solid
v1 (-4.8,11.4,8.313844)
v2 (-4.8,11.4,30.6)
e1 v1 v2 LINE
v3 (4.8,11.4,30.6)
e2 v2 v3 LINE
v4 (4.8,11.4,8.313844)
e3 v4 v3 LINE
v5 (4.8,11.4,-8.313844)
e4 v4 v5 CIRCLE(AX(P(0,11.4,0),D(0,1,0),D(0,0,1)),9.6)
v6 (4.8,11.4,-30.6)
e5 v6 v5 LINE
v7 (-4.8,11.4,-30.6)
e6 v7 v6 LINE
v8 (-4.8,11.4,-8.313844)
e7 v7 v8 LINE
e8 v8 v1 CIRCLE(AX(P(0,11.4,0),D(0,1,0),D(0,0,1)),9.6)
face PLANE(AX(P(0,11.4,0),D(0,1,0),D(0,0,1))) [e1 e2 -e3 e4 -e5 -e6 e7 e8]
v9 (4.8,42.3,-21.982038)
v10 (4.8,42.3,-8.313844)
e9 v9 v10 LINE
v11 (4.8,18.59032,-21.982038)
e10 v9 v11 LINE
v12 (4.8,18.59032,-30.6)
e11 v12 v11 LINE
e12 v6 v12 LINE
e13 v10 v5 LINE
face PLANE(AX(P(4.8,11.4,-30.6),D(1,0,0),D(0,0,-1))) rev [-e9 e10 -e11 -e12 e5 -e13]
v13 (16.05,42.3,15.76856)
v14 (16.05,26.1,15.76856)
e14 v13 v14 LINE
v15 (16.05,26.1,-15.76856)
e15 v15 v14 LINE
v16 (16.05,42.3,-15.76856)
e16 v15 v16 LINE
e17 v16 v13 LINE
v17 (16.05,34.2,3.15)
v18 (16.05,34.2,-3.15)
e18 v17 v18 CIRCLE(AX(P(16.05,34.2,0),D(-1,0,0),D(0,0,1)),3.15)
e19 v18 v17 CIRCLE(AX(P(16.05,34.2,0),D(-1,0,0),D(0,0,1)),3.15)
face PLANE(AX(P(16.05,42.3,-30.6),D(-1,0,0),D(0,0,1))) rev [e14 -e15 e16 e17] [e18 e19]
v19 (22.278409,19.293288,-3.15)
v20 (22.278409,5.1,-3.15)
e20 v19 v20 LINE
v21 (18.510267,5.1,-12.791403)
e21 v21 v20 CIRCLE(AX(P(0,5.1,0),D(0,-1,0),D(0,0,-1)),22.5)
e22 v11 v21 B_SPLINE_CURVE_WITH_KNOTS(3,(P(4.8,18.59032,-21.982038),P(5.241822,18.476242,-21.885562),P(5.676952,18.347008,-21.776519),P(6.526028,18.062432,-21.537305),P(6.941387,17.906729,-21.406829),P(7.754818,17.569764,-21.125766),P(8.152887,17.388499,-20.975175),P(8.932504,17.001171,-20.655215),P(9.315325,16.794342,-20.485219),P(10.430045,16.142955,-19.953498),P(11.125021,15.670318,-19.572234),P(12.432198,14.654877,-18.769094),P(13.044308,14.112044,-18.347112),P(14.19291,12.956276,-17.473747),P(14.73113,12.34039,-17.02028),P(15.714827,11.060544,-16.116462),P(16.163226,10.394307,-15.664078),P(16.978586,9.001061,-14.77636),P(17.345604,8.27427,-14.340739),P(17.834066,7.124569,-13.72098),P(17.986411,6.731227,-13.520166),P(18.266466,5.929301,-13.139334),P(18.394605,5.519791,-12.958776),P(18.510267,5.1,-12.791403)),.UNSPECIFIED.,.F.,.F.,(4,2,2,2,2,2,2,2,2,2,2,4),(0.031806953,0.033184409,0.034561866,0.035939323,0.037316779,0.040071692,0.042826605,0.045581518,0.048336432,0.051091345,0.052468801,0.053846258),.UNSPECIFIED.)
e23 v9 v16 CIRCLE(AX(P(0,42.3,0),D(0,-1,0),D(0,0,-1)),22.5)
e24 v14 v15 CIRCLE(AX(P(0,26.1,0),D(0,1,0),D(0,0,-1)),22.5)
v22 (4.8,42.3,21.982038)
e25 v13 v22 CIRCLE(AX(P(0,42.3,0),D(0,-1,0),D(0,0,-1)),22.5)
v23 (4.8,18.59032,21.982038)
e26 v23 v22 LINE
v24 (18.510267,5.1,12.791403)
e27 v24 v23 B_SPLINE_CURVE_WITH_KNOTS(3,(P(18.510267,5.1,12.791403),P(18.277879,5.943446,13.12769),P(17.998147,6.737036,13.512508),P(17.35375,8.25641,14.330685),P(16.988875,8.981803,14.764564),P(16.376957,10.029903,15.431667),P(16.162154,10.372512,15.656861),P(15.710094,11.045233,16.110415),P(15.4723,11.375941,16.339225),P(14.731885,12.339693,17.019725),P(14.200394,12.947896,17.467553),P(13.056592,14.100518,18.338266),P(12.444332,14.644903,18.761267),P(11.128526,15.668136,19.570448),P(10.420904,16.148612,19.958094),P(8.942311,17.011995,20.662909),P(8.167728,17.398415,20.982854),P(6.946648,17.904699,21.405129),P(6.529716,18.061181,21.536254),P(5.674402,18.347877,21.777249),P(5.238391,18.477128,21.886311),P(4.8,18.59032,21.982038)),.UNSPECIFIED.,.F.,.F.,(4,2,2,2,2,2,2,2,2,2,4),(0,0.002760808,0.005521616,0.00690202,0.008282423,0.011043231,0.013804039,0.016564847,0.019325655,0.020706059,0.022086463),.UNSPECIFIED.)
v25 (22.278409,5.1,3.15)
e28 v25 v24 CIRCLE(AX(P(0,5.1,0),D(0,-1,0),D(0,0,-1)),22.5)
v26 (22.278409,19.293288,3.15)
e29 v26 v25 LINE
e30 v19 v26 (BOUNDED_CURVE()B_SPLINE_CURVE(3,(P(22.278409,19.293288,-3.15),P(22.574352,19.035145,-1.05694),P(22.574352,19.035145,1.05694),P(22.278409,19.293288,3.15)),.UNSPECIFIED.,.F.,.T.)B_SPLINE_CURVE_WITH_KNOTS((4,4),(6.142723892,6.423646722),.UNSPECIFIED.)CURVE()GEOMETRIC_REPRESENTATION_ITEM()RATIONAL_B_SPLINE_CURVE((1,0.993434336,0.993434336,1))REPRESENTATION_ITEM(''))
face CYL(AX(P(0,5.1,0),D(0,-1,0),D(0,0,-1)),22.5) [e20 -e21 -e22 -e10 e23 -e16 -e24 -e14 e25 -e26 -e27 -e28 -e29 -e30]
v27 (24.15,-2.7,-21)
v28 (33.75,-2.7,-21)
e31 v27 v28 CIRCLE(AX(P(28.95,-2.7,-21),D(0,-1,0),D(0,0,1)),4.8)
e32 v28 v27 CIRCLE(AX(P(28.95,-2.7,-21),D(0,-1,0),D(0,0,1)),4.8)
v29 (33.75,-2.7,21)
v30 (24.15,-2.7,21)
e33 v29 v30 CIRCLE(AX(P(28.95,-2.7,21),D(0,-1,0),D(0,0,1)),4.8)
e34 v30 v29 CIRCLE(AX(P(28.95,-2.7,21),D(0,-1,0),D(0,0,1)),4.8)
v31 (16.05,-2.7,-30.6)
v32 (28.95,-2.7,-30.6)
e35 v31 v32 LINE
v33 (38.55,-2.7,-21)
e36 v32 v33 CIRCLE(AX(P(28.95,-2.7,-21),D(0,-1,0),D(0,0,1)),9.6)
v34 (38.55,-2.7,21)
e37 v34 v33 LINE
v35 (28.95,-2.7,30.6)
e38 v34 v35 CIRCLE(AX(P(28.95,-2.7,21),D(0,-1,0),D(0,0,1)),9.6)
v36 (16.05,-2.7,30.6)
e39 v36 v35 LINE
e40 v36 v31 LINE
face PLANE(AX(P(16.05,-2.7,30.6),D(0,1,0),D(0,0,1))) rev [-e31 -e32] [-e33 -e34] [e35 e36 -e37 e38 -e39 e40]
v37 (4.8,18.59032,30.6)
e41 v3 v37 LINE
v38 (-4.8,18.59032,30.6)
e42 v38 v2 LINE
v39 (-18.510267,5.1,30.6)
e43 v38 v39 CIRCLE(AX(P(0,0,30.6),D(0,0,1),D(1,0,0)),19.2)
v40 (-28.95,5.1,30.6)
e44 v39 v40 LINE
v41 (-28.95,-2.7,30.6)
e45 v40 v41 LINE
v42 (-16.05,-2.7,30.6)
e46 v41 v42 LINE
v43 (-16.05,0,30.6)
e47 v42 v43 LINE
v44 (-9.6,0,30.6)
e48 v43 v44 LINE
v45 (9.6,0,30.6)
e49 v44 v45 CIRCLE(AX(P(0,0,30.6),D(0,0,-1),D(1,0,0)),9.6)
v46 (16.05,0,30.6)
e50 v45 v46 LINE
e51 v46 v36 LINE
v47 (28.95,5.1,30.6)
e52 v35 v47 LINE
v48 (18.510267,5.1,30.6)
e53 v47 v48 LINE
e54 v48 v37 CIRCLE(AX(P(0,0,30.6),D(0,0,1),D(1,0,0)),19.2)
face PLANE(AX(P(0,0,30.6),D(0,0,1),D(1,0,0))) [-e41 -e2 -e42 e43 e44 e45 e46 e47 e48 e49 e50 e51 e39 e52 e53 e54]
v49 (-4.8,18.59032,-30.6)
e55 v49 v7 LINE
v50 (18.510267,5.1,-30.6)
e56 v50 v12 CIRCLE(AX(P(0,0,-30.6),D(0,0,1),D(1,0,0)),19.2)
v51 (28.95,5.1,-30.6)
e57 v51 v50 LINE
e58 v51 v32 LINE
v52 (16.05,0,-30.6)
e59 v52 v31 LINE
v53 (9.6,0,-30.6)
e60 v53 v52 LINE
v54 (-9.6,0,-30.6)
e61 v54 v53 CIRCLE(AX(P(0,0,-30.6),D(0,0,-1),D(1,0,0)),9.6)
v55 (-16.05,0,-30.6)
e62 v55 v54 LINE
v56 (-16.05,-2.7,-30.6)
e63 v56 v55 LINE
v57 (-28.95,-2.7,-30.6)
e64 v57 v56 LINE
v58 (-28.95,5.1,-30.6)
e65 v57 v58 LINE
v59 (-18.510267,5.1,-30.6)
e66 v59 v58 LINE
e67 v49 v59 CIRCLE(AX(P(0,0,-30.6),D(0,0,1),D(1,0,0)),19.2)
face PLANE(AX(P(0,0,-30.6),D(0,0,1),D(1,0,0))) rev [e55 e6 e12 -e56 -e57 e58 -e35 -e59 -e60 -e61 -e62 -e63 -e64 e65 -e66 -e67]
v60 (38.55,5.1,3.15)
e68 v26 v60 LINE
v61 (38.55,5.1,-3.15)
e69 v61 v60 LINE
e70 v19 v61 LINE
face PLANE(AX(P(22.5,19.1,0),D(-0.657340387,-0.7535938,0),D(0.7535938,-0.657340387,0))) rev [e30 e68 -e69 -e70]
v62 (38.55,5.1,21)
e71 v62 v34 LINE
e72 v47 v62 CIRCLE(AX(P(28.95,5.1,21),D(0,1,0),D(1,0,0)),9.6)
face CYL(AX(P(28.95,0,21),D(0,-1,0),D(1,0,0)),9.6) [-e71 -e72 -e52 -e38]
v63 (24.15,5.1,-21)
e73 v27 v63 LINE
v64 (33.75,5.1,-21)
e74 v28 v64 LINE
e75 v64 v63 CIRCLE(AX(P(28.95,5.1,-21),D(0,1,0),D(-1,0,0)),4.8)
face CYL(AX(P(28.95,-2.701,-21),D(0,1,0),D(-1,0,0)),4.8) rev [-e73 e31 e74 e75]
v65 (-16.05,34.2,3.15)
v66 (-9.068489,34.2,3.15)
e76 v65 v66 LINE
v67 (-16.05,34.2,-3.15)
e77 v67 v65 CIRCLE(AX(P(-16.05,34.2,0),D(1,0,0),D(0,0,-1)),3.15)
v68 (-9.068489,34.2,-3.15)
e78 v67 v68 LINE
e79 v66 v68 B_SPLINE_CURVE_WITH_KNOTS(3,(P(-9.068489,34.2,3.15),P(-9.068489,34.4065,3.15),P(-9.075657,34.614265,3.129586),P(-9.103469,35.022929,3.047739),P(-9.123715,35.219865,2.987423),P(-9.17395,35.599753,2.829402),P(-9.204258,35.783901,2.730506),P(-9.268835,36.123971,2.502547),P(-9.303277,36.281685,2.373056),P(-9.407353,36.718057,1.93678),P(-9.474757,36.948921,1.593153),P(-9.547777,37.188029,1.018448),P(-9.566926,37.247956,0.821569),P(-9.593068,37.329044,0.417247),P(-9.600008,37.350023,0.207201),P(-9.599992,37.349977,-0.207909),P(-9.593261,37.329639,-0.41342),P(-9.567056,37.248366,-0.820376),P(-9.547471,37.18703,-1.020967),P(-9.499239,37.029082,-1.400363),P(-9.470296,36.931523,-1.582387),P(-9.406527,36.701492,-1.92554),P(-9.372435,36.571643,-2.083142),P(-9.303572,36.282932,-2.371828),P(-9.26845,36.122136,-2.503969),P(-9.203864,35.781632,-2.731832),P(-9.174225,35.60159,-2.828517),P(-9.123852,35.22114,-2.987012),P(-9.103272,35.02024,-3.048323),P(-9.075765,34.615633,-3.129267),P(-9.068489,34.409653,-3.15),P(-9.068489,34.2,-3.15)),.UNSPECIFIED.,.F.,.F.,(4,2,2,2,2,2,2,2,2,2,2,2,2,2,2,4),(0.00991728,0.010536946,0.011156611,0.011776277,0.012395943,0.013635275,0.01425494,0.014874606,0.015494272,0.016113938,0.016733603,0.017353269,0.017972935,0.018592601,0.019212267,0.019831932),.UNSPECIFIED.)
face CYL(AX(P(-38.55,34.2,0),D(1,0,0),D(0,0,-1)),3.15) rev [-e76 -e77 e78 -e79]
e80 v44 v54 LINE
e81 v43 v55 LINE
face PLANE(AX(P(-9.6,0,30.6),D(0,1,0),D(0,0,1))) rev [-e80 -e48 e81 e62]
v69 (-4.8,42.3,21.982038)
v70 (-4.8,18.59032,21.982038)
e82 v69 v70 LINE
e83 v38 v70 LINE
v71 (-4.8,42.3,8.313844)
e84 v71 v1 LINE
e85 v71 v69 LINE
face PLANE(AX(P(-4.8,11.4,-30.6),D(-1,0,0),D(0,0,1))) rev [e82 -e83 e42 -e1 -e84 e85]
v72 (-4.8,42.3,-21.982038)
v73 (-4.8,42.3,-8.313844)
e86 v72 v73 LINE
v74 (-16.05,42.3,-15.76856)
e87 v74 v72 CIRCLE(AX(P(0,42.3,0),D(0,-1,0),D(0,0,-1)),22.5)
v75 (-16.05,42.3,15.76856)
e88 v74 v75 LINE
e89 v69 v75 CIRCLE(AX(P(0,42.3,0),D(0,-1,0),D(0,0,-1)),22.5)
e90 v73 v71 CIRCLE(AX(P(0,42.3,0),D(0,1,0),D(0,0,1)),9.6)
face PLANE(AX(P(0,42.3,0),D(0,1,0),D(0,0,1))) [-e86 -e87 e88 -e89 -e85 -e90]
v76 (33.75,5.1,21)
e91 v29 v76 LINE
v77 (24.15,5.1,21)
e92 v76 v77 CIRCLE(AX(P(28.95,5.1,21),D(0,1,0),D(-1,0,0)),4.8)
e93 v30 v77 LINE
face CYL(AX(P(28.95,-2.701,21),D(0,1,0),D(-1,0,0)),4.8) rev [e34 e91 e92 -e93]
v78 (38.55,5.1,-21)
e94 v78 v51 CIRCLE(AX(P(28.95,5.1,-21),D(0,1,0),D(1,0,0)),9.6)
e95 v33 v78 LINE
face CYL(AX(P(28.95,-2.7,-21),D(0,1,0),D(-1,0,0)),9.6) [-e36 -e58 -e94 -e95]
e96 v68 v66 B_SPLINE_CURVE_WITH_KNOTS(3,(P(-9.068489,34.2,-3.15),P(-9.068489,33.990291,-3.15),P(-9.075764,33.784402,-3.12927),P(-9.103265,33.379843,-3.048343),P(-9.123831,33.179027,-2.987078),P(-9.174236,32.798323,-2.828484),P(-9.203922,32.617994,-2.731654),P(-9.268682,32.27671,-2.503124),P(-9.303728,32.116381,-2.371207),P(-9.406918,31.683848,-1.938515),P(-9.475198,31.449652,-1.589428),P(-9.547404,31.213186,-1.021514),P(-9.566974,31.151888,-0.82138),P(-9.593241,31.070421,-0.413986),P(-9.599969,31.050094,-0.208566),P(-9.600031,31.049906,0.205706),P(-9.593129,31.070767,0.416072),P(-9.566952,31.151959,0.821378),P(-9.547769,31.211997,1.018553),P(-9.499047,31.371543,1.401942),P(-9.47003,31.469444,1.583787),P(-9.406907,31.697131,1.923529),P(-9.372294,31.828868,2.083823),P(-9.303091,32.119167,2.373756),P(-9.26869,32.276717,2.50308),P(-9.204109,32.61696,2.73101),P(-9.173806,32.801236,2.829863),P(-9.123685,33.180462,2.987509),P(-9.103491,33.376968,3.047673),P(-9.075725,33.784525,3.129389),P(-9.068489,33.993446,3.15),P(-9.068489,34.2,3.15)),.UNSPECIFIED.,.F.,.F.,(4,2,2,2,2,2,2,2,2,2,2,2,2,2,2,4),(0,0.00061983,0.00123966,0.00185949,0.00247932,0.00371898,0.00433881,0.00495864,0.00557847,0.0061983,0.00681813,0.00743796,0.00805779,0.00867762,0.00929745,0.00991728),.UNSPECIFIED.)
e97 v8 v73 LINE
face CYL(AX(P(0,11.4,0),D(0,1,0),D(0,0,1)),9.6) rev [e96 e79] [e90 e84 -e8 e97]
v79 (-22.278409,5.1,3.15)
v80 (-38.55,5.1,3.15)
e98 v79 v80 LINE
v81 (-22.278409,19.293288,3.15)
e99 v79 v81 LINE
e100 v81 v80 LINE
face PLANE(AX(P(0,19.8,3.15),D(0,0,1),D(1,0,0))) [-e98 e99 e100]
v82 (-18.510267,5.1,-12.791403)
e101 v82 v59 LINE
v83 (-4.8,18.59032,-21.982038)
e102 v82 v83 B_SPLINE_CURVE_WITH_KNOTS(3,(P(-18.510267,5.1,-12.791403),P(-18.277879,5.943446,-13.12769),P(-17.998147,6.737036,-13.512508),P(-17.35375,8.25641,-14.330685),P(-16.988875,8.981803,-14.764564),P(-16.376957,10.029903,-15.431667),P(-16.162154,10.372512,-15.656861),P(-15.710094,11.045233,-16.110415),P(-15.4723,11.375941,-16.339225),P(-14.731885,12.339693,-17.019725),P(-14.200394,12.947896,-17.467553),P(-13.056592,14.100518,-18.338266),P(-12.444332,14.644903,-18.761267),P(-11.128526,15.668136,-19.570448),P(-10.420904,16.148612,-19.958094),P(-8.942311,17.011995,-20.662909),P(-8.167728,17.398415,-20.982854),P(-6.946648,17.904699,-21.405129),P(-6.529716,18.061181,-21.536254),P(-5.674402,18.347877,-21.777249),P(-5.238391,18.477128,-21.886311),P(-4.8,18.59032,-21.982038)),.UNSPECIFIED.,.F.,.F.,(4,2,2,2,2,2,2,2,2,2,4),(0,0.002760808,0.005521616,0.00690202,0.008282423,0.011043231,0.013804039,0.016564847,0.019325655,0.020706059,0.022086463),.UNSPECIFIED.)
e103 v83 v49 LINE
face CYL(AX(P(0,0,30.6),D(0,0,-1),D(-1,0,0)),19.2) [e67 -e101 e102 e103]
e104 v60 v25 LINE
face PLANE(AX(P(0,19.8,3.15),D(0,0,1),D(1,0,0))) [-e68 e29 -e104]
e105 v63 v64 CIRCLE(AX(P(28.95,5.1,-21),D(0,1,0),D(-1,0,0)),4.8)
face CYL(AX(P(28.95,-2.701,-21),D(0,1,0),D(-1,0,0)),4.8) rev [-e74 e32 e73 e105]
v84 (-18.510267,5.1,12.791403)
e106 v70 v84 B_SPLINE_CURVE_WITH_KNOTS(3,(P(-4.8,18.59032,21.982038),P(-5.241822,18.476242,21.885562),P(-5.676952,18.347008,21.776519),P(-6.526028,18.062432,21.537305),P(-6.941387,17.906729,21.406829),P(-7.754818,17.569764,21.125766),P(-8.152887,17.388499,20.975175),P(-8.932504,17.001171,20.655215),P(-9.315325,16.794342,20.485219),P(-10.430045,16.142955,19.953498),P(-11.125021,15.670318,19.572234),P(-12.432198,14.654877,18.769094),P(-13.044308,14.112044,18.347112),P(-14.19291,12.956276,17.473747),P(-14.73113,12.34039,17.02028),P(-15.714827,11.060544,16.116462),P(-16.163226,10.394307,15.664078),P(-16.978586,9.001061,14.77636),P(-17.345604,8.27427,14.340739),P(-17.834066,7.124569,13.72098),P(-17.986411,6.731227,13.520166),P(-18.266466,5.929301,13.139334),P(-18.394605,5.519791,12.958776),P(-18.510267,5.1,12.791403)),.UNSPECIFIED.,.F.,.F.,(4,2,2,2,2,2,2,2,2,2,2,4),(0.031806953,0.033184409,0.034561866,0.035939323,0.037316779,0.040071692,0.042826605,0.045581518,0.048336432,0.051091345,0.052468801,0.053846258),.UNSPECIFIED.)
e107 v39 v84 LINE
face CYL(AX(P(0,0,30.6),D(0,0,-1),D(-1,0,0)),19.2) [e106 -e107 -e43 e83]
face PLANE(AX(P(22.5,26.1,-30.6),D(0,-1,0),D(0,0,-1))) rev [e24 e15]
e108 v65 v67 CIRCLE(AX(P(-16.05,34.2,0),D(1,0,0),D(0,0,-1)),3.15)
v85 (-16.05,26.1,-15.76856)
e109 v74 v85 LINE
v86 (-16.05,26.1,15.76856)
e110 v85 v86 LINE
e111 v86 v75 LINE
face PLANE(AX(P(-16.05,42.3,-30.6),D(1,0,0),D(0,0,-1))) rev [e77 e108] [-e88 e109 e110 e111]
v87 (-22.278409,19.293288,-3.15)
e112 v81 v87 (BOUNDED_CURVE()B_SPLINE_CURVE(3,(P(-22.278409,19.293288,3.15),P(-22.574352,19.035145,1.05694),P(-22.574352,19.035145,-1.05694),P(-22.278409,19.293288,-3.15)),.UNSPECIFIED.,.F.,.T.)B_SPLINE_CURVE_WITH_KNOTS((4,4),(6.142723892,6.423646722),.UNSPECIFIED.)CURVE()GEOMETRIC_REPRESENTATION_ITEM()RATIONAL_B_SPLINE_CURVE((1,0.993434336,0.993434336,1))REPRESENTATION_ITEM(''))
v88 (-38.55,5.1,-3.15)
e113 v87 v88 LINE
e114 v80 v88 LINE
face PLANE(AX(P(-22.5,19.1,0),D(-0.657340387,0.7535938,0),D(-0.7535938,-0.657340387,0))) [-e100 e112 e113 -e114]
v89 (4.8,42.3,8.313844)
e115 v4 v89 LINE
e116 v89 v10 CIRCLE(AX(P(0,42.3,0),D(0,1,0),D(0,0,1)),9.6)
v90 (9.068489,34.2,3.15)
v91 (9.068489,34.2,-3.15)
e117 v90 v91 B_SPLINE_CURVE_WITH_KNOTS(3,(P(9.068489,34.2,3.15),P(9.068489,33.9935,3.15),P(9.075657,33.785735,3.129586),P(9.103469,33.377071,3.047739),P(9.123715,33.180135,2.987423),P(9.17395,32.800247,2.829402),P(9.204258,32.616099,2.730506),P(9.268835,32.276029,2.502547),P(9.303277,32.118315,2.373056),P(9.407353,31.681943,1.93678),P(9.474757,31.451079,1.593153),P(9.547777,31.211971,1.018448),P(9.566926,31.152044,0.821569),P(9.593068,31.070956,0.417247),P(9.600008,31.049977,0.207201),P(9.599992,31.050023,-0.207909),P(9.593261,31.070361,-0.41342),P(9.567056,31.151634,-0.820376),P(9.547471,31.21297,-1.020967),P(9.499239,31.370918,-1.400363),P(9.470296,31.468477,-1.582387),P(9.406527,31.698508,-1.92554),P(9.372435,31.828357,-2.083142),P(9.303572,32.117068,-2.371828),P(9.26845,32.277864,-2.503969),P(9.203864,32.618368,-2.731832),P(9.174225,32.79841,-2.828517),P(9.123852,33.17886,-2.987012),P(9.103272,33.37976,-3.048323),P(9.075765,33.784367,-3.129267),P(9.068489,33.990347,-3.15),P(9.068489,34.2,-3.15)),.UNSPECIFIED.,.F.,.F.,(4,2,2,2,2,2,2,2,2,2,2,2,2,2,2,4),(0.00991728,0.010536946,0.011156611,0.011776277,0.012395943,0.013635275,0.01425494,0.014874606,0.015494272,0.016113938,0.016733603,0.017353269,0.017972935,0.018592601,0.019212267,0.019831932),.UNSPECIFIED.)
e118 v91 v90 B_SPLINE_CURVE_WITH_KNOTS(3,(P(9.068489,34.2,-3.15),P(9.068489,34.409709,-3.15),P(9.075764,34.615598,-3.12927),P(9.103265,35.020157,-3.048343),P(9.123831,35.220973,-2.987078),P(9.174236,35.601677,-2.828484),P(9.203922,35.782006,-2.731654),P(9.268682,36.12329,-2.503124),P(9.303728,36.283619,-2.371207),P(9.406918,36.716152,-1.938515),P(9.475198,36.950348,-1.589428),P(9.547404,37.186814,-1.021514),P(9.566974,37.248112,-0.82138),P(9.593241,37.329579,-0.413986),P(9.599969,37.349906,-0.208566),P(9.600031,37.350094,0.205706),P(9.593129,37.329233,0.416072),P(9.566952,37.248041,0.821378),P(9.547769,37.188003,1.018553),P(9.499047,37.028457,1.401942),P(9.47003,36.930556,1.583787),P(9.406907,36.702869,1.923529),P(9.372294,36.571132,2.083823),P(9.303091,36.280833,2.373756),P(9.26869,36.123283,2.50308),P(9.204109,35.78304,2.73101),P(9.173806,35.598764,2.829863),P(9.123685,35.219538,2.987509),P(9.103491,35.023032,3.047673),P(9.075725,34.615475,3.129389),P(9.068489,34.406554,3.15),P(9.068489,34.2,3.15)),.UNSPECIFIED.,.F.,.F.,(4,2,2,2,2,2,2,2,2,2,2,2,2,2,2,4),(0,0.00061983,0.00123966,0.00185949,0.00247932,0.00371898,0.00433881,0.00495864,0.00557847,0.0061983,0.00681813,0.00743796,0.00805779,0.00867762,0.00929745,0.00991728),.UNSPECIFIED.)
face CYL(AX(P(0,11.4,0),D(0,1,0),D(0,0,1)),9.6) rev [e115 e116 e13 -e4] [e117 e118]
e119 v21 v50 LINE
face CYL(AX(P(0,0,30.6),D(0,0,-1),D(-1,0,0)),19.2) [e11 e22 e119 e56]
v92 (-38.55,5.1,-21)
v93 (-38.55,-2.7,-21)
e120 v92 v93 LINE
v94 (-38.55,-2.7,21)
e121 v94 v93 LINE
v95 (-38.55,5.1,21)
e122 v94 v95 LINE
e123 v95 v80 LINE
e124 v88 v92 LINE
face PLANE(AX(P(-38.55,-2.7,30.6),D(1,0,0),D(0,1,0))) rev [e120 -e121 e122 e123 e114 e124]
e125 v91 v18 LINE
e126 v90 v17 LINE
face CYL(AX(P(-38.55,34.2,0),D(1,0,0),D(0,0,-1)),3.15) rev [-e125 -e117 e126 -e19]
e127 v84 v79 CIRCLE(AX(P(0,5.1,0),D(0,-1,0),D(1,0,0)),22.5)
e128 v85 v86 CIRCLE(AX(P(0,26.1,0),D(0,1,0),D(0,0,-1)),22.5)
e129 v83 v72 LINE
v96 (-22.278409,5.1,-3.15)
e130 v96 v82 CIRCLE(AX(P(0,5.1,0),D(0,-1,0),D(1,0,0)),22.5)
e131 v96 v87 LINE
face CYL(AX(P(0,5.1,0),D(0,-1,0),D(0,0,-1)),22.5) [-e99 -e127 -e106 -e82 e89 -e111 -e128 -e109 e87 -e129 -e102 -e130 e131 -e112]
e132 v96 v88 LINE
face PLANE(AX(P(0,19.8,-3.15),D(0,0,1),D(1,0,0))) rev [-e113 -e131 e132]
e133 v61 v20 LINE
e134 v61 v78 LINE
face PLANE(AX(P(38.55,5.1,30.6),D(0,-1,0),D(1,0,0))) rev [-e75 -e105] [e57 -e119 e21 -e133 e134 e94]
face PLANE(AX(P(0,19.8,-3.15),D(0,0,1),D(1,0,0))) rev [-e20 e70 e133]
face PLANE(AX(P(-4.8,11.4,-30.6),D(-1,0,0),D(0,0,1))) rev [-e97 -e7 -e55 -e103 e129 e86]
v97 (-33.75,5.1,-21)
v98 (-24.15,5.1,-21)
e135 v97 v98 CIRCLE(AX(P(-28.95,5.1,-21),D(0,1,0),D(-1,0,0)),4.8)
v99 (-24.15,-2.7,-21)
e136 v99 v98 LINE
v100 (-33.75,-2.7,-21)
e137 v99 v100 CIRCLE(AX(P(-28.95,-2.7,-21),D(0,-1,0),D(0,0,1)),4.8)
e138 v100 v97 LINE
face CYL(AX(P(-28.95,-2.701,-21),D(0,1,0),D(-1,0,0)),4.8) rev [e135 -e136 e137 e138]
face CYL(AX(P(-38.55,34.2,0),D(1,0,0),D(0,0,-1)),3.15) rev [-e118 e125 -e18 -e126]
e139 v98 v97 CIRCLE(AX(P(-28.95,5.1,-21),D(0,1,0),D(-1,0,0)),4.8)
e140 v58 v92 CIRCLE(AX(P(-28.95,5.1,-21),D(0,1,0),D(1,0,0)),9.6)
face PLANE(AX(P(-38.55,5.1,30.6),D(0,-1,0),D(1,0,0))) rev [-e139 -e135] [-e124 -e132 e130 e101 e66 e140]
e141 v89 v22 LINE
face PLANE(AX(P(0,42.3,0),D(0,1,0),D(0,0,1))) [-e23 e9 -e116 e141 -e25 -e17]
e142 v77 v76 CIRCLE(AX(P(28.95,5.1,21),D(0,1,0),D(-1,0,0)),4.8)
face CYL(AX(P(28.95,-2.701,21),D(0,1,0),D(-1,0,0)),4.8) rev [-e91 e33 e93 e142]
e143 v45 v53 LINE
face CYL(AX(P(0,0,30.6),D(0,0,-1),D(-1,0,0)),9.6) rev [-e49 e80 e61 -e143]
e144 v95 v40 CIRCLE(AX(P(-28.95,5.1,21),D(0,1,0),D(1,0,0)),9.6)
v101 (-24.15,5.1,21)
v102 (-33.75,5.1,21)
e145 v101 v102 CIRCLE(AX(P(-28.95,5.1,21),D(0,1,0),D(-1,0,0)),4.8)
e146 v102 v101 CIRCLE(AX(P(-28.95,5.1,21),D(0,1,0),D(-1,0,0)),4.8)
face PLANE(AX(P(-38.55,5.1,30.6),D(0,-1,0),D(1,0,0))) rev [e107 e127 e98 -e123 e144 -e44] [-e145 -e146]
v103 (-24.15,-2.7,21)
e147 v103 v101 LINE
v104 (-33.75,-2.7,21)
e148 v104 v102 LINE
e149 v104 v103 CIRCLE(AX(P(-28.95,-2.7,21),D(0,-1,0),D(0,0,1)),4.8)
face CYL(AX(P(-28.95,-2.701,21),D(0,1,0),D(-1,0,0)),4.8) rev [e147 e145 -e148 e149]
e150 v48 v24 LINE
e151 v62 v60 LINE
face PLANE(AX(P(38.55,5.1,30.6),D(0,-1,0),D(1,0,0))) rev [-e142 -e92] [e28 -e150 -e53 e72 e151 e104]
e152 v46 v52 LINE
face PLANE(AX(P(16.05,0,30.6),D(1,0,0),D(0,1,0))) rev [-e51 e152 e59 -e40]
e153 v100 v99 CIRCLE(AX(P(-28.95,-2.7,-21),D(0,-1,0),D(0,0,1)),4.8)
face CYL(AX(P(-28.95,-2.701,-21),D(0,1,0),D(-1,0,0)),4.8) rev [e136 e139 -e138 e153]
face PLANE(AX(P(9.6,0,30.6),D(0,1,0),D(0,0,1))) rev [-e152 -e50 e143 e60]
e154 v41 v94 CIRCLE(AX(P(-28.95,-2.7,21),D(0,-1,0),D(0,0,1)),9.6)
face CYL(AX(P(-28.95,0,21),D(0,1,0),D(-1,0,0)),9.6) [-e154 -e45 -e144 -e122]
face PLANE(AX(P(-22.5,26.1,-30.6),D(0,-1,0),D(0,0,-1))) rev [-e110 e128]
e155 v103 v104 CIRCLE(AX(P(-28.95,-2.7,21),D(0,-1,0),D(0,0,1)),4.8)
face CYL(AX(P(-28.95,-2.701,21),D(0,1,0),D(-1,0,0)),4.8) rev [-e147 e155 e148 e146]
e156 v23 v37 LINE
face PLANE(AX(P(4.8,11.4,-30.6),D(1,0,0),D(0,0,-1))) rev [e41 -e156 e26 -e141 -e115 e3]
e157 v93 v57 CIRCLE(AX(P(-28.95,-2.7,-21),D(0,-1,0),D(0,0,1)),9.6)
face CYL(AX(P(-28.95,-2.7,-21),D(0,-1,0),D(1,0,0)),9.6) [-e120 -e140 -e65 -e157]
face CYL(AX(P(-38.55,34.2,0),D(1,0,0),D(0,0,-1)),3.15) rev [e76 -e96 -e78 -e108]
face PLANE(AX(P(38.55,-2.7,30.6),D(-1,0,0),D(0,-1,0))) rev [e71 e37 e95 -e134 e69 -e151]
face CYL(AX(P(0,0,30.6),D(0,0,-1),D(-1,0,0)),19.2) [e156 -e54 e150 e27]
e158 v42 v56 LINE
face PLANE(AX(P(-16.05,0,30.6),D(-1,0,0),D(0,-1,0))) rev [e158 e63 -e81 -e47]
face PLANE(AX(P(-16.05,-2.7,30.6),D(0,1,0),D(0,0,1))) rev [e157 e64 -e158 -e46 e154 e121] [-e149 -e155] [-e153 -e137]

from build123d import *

# Parameters (mm, degrees)
BASE_BODY_DEPTH                 = 30.6
BASE_CORNER_FILLETS_R9_6_R      = 9.6
MOUNTING_HOLES_4X_9_6_REACH     = 53.198
MOUNTING_HOLES_SKETCH_R         = 4.8
BEARING_HUB_PROFILE_SKETCH_W    = 22.5
BEARING_HUB_PROFILE_SKETCH_H    = 37.2
BORE_SKETCH_R                   = 9.6
BORE_19_2_DEPTH                 = 30.9
BASE_RELIEF_CUT_DEPTH           = 84.790408286
CLAMP_SLOT_SKETCH_W             = 9.6
CLAMP_SLOT_SKETCH_H             = 30.9
CLAMP_SLOT_9_6_DEPTH            = 84.790408286
SUPPORT_RIB_6_3_REACH           = 66.898
SUPPORT_RIB_SKETCH_WALL_W       = 153.093978432
SUPPORT_RIB_SKETCH_WALL_H       = 6.3
HUB_SIDE_RELIEF_CUT_DEPTH       = 65.898016261
HUB_SIDE_RELIEF_CUT_DEPTH_BACK  = 65.898016261
HUB_SIDE_RELIEF_SKETCH_W        = 6.45
HUB_SIDE_RELIEF_SKETCH_H        = 16.2
CLAMP_SCREW_HOLE_6_3_DEPTH      = 65.898016261
CLAMP_SCREW_HOLE_6_3_DEPTH_BACK = 65.898016261
CLAMP_SCREW_HOLE_SKETCH_R       = 3.15


with BuildPart() as part:
    # Base Body Profile Sketch → Base Body (new, symmetric)
    with BuildSketch(Plane.XY):
        with BuildLine():
            Line((9.6, 0), (16.05, 0))
            Line((16.05, 0), (16.05, -2.7))
            Line((16.05, -2.7), (38.55, -2.7))
            Line((38.55, -2.7), (38.55, 5.1))
            Line((38.55, 5.1), (18.510267421, 5.1))
            ThreePointArc((18.510267421, 5.1), (0, 19.2), (-18.510267421, 5.1))
            Line((-18.510267421, 5.1), (-38.55, 5.1))
            Line((-38.55, 5.1), (-38.55, -2.7))
            Line((-38.55, -2.7), (-16.05, -2.7))
            Line((-16.05, -2.7), (-16.05, 0))
            Line((-16.05, 0), (-9.6, 0))
            ThreePointArc((-9.6, 0), (0, 9.6), (9.6, 0))
        make_face()
    extrude(amount=BASE_BODY_DEPTH, both=True)

    # Base Corner Fillets R9.6
    base_corner_fillets_r9_6_edges = [part.edges().sort_by_distance(p)[0] for p in [
        (-38.55, 1.2, -30.6),
        (38.55, 1.2, -30.6),
        (38.55, 1.2, 30.6),
        (-38.55, 1.2, 30.6),
    ]]
    fillet(base_corner_fillets_r9_6_edges, radius=BASE_CORNER_FILLETS_R9_6_R)

    # Mounting Holes Sketch → Mounting Holes 4xØ9.6 (cut, up to next)
    with BuildSketch(Plane(origin=(0, 5.1, 0), x_dir=(1, 0, 0), z_dir=(0, 1, 0)), mode=Mode.PRIVATE) as mounting_holes_4x_9_6_sk1:
        with Locations(Location((-28.95, 21, 0), (0, 0, 180))):
            Circle(MOUNTING_HOLES_SKETCH_R)
    mounting_holes_4x_9_6_tool1 = extrude(mounting_holes_4x_9_6_sk1.sketch, amount=-MOUNTING_HOLES_4X_9_6_REACH, mode=Mode.PRIVATE) & part.part
    # Mounting Holes Sketch → Mounting Holes 4xØ9.6 (cut, up to next)
    with BuildSketch(Plane(origin=(0, 5.1, 0), x_dir=(1, 0, 0), z_dir=(0, 1, 0)), mode=Mode.PRIVATE) as mounting_holes_4x_9_6_sk2:
        with Locations(Location((-28.95, -21, 0), (0, 0, 180))):
            Circle(MOUNTING_HOLES_SKETCH_R)
    mounting_holes_4x_9_6_tool2 = extrude(mounting_holes_4x_9_6_sk2.sketch, amount=-MOUNTING_HOLES_4X_9_6_REACH, mode=Mode.PRIVATE) & part.part
    # Mounting Holes Sketch → Mounting Holes 4xØ9.6 (cut, up to next)
    with BuildSketch(Plane(origin=(0, 5.1, 0), x_dir=(1, 0, 0), z_dir=(0, 1, 0)), mode=Mode.PRIVATE) as mounting_holes_4x_9_6_sk3:
        with Locations(Location((28.95, -21, 0), (0, 0, 180))):
            Circle(MOUNTING_HOLES_SKETCH_R)
    mounting_holes_4x_9_6_tool3 = extrude(mounting_holes_4x_9_6_sk3.sketch, amount=-MOUNTING_HOLES_4X_9_6_REACH, mode=Mode.PRIVATE) & part.part
    # Mounting Holes Sketch → Mounting Holes 4xØ9.6 (cut, up to next)
    with BuildSketch(Plane(origin=(0, 5.1, 0), x_dir=(1, 0, 0), z_dir=(0, 1, 0)), mode=Mode.PRIVATE) as mounting_holes_4x_9_6_sk4:
        with Locations(Location((28.95, 21, 0), (0, 0, 180))):
            Circle(MOUNTING_HOLES_SKETCH_R)
    mounting_holes_4x_9_6_tool4 = extrude(mounting_holes_4x_9_6_sk4.sketch, amount=-MOUNTING_HOLES_4X_9_6_REACH, mode=Mode.PRIVATE) & part.part
    add(mounting_holes_4x_9_6_tool1.solids().sort_by_distance((-28.95, 5.1, -21))[0], mode=Mode.SUBTRACT)
    add(mounting_holes_4x_9_6_tool2.solids().sort_by_distance((-28.95, 5.1, 21))[0], mode=Mode.SUBTRACT)
    add(mounting_holes_4x_9_6_tool3.solids().sort_by_distance((28.95, 5.1, 21))[0], mode=Mode.SUBTRACT)
    add(mounting_holes_4x_9_6_tool4.solids().sort_by_distance((28.95, 5.1, -21))[0], mode=Mode.SUBTRACT)

    # Bearing Hub Profile Sketch → Bearing Hub Ø45 (revolve)
    with BuildSketch(Plane.XY, mode=Mode.PRIVATE) as bearing_hub_45_sk:
        with Locations((11.25, 23.7)):
            Rectangle(BEARING_HUB_PROFILE_SKETCH_W, BEARING_HUB_PROFILE_SKETCH_H)
    revolve(bearing_hub_45_sk.sketch.rotate(Axis((0, 5.1, 0), (0, 1, 0)), 90), axis=Axis((0, 5.1, 0), (0, 1, 0)))

    # Bore Sketch → Bore Ø19.2 (cut)
    with BuildSketch(Plane(origin=(0, 42.3, 0), x_dir=(1, 0, 0), z_dir=(0, 1, 0))):
        with Locations(Location((0, 0, 0), (0, 0, 270))):
            Circle(BORE_SKETCH_R)
    extrude(amount=-BORE_19_2_DEPTH, mode=Mode.SUBTRACT)

    # Base Relief Sketch → Base Relief Cut (cut, through all)
    with BuildSketch(Plane.XY.offset(30.6)):
        with BuildLine():
            Line((-9.6, 0), (9.6, 0))
            ThreePointArc((9.6, 0), (0, 9.6), (-9.6, 0))
        make_face()
    extrude(amount=-BASE_RELIEF_CUT_DEPTH, mode=Mode.SUBTRACT)

    # Clamp Slot Sketch → Clamp Slot 9.6 (cut, through all)
    with BuildSketch(Plane.XY.offset(30.6)):
        with Locations((0, 26.85)):
            Rectangle(CLAMP_SLOT_SKETCH_W, CLAMP_SLOT_SKETCH_H)
    extrude(amount=-CLAMP_SLOT_9_6_DEPTH, mode=Mode.SUBTRACT)

    # Support Rib Sketch wall → Support Rib 6.3 (add, up to next)
    with BuildSketch(Plane(origin=(-30.525, 12.1, 0), x_dir=(-0.753593800433, -0.657340386671, 0), z_dir=(0.657340386671, -0.753593800433, 0)), mode=Mode.PRIVATE) as support_rib_6_3_sk1:
        Rectangle(SUPPORT_RIB_SKETCH_WALL_W, SUPPORT_RIB_SKETCH_WALL_H)
    support_rib_6_3_tool1 = extrude(support_rib_6_3_sk1.sketch, amount=SUPPORT_RIB_6_3_REACH, mode=Mode.PRIVATE) - part.part
    support_rib_6_3 = support_rib_6_3_tool1.solids().sort_by_distance((-30.525, 12.1, 0))[0]
    add(support_rib_6_3)

    # Support Rib Mirror: Support Rib 6.3 across plane
    add(support_rib_6_3.mirror(Plane(origin=(0, 0, 0), x_dir=(0, 0, 1), z_dir=(1, 0, 0))))

    # Hub Side Relief Sketch → Hub Side Relief Cut (cut, two sides: drawn at the far end of the back side and taken through both)
    with BuildSketch(Plane.XY.offset(-HUB_SIDE_RELIEF_CUT_DEPTH_BACK)):
        with Locations((-19.275, 34.2)):
            Rectangle(HUB_SIDE_RELIEF_SKETCH_W, HUB_SIDE_RELIEF_SKETCH_H)
        with Locations((19.275, 34.2)):
            Rectangle(HUB_SIDE_RELIEF_SKETCH_W, HUB_SIDE_RELIEF_SKETCH_H)
    extrude(amount=HUB_SIDE_RELIEF_CUT_DEPTH + HUB_SIDE_RELIEF_CUT_DEPTH_BACK, mode=Mode.SUBTRACT)

    # Clamp Screw Hole Sketch → Clamp Screw Hole Ø6.3 (cut, two sides: drawn at the far end of the back side and taken through both)
    with BuildSketch(Plane(origin=(0, 0, 0), x_dir=(0, 0, -1), z_dir=(1, 0, 0)).offset(-CLAMP_SCREW_HOLE_6_3_DEPTH_BACK)):
        with Locations((0, 34.2)):
            Circle(CLAMP_SCREW_HOLE_SKETCH_R)
    extrude(amount=CLAMP_SCREW_HOLE_6_3_DEPTH + CLAMP_SCREW_HOLE_6_3_DEPTH_BACK, mode=Mode.SUBTRACT)


solid = part.part
